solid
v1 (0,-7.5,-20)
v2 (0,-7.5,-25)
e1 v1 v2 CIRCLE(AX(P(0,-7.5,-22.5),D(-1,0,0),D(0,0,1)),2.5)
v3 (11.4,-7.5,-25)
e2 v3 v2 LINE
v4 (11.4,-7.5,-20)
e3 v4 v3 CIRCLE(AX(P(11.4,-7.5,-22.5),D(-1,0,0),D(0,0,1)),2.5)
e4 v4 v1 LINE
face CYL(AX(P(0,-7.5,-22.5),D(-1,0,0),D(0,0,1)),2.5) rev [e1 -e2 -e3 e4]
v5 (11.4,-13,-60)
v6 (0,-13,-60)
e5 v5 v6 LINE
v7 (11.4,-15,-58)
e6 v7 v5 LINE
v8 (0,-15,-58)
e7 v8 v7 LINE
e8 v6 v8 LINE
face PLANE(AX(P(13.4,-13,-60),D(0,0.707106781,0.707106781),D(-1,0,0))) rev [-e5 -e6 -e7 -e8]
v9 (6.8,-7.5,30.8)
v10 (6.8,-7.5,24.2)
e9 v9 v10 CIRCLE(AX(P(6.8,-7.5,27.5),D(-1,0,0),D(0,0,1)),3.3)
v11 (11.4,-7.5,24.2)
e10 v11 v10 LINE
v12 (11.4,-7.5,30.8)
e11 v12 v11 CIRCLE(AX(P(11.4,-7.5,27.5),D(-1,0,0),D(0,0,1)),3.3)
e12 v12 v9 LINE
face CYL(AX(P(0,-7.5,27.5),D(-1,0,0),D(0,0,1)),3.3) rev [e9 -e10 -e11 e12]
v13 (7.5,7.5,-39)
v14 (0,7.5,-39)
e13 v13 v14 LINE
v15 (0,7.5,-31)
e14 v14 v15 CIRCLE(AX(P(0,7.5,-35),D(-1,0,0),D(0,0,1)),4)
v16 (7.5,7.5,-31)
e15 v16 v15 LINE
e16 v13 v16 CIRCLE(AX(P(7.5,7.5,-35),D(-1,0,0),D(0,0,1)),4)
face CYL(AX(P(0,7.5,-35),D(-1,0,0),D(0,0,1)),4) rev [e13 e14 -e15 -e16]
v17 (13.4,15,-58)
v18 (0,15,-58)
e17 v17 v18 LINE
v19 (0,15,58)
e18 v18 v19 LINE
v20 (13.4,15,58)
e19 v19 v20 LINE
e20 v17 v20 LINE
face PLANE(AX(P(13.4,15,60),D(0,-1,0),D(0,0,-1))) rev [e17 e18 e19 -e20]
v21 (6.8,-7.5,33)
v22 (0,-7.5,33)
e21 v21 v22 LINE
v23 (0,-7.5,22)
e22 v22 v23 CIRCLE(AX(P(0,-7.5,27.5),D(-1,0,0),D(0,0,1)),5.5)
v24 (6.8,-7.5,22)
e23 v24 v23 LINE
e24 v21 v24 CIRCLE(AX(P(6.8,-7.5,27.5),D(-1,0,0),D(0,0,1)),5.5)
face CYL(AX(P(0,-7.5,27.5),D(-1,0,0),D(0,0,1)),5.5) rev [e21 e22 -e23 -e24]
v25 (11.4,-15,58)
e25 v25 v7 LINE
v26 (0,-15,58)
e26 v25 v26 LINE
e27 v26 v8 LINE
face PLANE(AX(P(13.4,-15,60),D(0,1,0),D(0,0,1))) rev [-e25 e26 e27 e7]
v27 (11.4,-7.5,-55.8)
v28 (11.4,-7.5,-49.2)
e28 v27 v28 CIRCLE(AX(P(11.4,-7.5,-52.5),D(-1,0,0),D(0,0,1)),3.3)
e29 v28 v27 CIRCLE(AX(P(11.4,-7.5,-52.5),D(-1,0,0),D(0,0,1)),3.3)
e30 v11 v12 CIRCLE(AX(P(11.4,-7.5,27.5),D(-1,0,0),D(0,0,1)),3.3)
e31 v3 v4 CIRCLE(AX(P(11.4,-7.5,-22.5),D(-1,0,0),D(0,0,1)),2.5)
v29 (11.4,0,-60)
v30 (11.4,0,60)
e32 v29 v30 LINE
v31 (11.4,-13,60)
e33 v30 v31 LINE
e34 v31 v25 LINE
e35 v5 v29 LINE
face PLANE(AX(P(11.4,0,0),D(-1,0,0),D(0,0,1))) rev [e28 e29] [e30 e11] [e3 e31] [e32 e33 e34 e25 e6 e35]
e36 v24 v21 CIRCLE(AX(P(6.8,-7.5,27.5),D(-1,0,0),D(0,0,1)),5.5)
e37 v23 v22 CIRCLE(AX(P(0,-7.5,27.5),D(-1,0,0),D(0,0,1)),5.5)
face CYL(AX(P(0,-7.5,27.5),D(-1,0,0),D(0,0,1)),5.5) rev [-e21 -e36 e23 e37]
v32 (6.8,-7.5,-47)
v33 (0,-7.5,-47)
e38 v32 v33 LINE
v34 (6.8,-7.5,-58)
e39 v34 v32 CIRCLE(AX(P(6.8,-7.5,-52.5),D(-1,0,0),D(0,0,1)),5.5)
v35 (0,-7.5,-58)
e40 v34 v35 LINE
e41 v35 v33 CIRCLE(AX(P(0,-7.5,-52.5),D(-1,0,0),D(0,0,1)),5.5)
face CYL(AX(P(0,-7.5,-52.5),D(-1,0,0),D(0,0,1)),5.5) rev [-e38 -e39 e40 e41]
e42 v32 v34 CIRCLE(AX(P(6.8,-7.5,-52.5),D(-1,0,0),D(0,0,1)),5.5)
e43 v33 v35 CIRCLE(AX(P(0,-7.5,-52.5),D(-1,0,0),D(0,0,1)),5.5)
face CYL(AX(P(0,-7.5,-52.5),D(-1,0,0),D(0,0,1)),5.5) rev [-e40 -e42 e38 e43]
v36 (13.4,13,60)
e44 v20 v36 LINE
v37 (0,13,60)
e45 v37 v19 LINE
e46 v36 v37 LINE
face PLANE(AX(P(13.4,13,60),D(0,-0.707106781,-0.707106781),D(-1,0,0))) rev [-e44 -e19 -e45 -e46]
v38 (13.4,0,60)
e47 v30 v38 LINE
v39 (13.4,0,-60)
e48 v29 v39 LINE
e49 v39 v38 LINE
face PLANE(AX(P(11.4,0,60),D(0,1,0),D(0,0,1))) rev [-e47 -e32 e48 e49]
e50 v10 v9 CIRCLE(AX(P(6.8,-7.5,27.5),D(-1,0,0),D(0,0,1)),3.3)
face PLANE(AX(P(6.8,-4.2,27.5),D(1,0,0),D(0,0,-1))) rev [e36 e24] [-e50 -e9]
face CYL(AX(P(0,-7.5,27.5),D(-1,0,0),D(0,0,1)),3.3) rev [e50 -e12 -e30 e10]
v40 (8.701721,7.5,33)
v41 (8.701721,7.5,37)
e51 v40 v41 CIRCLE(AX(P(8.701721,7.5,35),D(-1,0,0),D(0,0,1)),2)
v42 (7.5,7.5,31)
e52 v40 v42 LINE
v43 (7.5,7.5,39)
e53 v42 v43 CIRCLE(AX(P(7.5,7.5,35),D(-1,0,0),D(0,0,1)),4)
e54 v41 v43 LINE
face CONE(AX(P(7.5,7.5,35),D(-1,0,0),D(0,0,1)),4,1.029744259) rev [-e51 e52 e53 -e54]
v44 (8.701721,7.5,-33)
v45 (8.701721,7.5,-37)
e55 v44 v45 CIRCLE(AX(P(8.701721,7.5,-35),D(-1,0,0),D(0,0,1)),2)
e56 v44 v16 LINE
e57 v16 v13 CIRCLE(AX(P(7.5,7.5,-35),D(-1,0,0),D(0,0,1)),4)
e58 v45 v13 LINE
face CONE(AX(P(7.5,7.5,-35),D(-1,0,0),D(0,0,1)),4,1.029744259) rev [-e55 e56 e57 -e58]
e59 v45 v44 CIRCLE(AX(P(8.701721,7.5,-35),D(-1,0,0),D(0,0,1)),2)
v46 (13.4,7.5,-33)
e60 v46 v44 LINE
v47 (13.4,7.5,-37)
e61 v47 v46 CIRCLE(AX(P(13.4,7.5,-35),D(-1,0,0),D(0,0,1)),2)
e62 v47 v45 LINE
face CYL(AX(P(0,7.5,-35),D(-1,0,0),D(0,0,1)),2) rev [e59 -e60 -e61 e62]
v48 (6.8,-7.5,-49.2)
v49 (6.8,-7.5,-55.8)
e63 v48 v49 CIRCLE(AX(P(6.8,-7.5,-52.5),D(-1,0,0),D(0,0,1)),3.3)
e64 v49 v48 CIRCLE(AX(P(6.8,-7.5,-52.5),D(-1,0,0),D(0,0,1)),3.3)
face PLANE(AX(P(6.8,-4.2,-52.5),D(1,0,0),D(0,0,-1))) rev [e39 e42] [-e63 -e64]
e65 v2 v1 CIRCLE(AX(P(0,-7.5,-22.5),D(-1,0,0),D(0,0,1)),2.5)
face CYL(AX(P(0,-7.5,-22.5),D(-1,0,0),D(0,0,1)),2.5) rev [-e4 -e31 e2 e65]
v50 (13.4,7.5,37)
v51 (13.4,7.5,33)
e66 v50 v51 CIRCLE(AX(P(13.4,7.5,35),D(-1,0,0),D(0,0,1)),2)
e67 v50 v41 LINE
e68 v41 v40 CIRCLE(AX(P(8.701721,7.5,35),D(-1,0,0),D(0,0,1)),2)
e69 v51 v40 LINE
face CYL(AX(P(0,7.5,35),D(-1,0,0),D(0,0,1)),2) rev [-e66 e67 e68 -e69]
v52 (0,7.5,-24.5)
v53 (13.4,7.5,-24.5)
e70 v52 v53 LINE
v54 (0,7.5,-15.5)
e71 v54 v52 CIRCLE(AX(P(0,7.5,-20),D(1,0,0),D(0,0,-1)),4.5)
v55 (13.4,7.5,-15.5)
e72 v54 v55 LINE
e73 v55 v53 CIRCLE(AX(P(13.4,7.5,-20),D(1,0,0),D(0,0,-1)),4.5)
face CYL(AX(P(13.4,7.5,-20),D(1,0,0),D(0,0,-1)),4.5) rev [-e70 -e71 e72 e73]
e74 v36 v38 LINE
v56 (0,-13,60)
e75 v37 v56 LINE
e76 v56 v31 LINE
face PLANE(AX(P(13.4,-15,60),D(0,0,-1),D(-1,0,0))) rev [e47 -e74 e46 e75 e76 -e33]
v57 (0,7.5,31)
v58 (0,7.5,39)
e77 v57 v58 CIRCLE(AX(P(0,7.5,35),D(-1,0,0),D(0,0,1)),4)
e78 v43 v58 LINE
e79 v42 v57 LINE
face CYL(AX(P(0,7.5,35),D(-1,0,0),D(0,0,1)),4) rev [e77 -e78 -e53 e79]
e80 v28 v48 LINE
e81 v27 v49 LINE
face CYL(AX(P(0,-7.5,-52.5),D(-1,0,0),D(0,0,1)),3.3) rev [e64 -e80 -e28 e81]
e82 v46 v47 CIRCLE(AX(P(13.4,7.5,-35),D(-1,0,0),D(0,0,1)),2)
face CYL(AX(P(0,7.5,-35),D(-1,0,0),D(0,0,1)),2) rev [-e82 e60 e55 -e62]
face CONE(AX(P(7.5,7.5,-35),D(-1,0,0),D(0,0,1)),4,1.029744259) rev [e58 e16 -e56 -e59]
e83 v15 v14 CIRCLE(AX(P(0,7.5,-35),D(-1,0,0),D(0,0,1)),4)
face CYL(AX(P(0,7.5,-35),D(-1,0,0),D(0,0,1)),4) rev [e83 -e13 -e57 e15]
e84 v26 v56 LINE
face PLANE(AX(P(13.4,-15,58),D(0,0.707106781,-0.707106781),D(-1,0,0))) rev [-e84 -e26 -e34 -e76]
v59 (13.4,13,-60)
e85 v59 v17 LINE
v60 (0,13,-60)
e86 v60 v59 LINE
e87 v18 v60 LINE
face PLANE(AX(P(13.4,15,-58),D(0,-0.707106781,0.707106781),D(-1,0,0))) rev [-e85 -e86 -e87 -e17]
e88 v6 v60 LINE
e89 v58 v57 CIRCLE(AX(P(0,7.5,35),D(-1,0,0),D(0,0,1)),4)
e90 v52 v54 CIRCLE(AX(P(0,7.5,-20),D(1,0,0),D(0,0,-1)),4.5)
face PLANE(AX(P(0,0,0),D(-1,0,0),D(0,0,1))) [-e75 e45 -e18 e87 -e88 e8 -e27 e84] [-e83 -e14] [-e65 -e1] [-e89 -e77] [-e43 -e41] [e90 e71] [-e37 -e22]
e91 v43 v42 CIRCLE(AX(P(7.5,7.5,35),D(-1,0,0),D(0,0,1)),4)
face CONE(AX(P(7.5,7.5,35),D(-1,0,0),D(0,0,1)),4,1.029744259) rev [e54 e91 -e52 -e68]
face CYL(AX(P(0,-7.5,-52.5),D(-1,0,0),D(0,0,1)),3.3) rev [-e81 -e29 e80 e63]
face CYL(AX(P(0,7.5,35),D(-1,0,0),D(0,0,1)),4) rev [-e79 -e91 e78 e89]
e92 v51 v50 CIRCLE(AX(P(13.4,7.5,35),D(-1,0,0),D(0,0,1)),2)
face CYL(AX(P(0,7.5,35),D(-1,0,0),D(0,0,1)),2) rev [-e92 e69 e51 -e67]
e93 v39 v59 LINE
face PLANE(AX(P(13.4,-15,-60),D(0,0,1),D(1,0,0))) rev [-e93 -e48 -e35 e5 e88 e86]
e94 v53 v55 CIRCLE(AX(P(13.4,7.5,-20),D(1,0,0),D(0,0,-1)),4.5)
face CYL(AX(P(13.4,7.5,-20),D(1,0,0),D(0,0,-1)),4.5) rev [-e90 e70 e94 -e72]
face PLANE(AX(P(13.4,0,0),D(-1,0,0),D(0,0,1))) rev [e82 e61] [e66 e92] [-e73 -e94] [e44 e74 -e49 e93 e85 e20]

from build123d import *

# Parameters (mm, degrees)
SKETCH1_W                                            = 120
SKETCH1_H                                            = 30
BOSS_EXTRUDE1_DEPTH                                  = 13.4
SKETCH2_W                                            = 120
SKETCH2_H                                            = 15
CUT_EXTRUDE1_DEPTH                                   = 2
HOLE1_AT_2_COUNT                                     = 2
HOLE1_AT_2_PITCH                                     = 70
M8_CLEARANCE_HOLE1_D                                 = 9
CHAMFER1_SIZE                                        = 2
CBORE_FOR_M6_HEXAGON_SOCKET_HEAD_CAP_SCR_D           = 6.6
CBORE_FOR_M6_HEXAGON_SOCKET_HEAD_CAP_SCR_CBORE_D     = 11
CBORE_FOR_M6_HEXAGON_SOCKET_HEAD_CAP_SCR_CBORE_DEPTH = 6.8
F_5_0MM_BLIND_HOLE_1_D                               = 5


with BuildPart() as part:
    # Sketch1 → Boss-Extrude1 (new body)
    with BuildSketch(Plane(origin=(0, 0, 0), x_dir=(0, 0, -1), z_dir=(1, 0, 0))):
        Rectangle(SKETCH1_W, SKETCH1_H)
    extrude(amount=BOSS_EXTRUDE1_DEPTH)

    # Sketch2 → Cut-Extrude1 (cut)
    with BuildSketch(Plane(origin=(13.4, 0, 0), x_dir=(0, 0, -1), z_dir=(1, 0, 0))):
        with Locations((0, -7.5)):
            Rectangle(SKETCH2_W, SKETCH2_H)
    extrude(amount=-CUT_EXTRUDE1_DEPTH, mode=Mode.SUBTRACT)

    # Sketch4 → Hole1 (revolve, cut)
    with BuildSketch(Plane(origin=(0, 7.5, 35), x_dir=(0, 0, 1), z_dir=(0, 1, 0))):
        Polygon((0, 0), (0, 20), (2, 20), (2, 8.701721238), (4, 7.5), (4, 0), align=None)
    hole1 = revolve(axis=Axis((-6.130023899, 7.5, 35), (1, 0, 0)), mode=Mode.SUBTRACT)

    # Hole1 at 2: Hole1 ×2
    with Locations(*[(0, 0, -i * HOLE1_AT_2_PITCH) for i in range(1, HOLE1_AT_2_COUNT)]):
        add(hole1, mode=Mode.SUBTRACT)

    # M8 Clearance Hole1 (through all)
    with Locations(Plane(origin=(13.4, 0, 0), x_dir=(0, 0, -1), z_dir=(1, 0, 0))):
        with Locations((20, 7.5)):
            Hole(M8_CLEARANCE_HOLE1_D / 2)

    # Chamfer1
    chamfer1_edges = [part.edges().sort_by_distance(p)[0] for p in [
        (5.7, -15, -60),
        (5.7, -15, 60),
        (6.7, 15, 60),
        (6.7, 15, -60),
    ]]
    chamfer(chamfer1_edges, length=CHAMFER1_SIZE)

    # CBORE for M6 Hexagon socket head cap screws1 (through all)
    with Locations(Plane.ZY):
        with Locations((-52.5, -7.5), (27.5, -7.5)):
            CounterBoreHole(CBORE_FOR_M6_HEXAGON_SOCKET_HEAD_CAP_SCR_D / 2, CBORE_FOR_M6_HEXAGON_SOCKET_HEAD_CAP_SCR_CBORE_D / 2, CBORE_FOR_M6_HEXAGON_SOCKET_HEAD_CAP_SCR_CBORE_DEPTH)

    # Ø5.0mm blind hole 1 (through all)
    with Locations(Plane.ZY):
        with Locations((-22.5, -7.5)):
            Hole(F_5_0MM_BLIND_HOLE_1_D / 2)


solid = part.part
